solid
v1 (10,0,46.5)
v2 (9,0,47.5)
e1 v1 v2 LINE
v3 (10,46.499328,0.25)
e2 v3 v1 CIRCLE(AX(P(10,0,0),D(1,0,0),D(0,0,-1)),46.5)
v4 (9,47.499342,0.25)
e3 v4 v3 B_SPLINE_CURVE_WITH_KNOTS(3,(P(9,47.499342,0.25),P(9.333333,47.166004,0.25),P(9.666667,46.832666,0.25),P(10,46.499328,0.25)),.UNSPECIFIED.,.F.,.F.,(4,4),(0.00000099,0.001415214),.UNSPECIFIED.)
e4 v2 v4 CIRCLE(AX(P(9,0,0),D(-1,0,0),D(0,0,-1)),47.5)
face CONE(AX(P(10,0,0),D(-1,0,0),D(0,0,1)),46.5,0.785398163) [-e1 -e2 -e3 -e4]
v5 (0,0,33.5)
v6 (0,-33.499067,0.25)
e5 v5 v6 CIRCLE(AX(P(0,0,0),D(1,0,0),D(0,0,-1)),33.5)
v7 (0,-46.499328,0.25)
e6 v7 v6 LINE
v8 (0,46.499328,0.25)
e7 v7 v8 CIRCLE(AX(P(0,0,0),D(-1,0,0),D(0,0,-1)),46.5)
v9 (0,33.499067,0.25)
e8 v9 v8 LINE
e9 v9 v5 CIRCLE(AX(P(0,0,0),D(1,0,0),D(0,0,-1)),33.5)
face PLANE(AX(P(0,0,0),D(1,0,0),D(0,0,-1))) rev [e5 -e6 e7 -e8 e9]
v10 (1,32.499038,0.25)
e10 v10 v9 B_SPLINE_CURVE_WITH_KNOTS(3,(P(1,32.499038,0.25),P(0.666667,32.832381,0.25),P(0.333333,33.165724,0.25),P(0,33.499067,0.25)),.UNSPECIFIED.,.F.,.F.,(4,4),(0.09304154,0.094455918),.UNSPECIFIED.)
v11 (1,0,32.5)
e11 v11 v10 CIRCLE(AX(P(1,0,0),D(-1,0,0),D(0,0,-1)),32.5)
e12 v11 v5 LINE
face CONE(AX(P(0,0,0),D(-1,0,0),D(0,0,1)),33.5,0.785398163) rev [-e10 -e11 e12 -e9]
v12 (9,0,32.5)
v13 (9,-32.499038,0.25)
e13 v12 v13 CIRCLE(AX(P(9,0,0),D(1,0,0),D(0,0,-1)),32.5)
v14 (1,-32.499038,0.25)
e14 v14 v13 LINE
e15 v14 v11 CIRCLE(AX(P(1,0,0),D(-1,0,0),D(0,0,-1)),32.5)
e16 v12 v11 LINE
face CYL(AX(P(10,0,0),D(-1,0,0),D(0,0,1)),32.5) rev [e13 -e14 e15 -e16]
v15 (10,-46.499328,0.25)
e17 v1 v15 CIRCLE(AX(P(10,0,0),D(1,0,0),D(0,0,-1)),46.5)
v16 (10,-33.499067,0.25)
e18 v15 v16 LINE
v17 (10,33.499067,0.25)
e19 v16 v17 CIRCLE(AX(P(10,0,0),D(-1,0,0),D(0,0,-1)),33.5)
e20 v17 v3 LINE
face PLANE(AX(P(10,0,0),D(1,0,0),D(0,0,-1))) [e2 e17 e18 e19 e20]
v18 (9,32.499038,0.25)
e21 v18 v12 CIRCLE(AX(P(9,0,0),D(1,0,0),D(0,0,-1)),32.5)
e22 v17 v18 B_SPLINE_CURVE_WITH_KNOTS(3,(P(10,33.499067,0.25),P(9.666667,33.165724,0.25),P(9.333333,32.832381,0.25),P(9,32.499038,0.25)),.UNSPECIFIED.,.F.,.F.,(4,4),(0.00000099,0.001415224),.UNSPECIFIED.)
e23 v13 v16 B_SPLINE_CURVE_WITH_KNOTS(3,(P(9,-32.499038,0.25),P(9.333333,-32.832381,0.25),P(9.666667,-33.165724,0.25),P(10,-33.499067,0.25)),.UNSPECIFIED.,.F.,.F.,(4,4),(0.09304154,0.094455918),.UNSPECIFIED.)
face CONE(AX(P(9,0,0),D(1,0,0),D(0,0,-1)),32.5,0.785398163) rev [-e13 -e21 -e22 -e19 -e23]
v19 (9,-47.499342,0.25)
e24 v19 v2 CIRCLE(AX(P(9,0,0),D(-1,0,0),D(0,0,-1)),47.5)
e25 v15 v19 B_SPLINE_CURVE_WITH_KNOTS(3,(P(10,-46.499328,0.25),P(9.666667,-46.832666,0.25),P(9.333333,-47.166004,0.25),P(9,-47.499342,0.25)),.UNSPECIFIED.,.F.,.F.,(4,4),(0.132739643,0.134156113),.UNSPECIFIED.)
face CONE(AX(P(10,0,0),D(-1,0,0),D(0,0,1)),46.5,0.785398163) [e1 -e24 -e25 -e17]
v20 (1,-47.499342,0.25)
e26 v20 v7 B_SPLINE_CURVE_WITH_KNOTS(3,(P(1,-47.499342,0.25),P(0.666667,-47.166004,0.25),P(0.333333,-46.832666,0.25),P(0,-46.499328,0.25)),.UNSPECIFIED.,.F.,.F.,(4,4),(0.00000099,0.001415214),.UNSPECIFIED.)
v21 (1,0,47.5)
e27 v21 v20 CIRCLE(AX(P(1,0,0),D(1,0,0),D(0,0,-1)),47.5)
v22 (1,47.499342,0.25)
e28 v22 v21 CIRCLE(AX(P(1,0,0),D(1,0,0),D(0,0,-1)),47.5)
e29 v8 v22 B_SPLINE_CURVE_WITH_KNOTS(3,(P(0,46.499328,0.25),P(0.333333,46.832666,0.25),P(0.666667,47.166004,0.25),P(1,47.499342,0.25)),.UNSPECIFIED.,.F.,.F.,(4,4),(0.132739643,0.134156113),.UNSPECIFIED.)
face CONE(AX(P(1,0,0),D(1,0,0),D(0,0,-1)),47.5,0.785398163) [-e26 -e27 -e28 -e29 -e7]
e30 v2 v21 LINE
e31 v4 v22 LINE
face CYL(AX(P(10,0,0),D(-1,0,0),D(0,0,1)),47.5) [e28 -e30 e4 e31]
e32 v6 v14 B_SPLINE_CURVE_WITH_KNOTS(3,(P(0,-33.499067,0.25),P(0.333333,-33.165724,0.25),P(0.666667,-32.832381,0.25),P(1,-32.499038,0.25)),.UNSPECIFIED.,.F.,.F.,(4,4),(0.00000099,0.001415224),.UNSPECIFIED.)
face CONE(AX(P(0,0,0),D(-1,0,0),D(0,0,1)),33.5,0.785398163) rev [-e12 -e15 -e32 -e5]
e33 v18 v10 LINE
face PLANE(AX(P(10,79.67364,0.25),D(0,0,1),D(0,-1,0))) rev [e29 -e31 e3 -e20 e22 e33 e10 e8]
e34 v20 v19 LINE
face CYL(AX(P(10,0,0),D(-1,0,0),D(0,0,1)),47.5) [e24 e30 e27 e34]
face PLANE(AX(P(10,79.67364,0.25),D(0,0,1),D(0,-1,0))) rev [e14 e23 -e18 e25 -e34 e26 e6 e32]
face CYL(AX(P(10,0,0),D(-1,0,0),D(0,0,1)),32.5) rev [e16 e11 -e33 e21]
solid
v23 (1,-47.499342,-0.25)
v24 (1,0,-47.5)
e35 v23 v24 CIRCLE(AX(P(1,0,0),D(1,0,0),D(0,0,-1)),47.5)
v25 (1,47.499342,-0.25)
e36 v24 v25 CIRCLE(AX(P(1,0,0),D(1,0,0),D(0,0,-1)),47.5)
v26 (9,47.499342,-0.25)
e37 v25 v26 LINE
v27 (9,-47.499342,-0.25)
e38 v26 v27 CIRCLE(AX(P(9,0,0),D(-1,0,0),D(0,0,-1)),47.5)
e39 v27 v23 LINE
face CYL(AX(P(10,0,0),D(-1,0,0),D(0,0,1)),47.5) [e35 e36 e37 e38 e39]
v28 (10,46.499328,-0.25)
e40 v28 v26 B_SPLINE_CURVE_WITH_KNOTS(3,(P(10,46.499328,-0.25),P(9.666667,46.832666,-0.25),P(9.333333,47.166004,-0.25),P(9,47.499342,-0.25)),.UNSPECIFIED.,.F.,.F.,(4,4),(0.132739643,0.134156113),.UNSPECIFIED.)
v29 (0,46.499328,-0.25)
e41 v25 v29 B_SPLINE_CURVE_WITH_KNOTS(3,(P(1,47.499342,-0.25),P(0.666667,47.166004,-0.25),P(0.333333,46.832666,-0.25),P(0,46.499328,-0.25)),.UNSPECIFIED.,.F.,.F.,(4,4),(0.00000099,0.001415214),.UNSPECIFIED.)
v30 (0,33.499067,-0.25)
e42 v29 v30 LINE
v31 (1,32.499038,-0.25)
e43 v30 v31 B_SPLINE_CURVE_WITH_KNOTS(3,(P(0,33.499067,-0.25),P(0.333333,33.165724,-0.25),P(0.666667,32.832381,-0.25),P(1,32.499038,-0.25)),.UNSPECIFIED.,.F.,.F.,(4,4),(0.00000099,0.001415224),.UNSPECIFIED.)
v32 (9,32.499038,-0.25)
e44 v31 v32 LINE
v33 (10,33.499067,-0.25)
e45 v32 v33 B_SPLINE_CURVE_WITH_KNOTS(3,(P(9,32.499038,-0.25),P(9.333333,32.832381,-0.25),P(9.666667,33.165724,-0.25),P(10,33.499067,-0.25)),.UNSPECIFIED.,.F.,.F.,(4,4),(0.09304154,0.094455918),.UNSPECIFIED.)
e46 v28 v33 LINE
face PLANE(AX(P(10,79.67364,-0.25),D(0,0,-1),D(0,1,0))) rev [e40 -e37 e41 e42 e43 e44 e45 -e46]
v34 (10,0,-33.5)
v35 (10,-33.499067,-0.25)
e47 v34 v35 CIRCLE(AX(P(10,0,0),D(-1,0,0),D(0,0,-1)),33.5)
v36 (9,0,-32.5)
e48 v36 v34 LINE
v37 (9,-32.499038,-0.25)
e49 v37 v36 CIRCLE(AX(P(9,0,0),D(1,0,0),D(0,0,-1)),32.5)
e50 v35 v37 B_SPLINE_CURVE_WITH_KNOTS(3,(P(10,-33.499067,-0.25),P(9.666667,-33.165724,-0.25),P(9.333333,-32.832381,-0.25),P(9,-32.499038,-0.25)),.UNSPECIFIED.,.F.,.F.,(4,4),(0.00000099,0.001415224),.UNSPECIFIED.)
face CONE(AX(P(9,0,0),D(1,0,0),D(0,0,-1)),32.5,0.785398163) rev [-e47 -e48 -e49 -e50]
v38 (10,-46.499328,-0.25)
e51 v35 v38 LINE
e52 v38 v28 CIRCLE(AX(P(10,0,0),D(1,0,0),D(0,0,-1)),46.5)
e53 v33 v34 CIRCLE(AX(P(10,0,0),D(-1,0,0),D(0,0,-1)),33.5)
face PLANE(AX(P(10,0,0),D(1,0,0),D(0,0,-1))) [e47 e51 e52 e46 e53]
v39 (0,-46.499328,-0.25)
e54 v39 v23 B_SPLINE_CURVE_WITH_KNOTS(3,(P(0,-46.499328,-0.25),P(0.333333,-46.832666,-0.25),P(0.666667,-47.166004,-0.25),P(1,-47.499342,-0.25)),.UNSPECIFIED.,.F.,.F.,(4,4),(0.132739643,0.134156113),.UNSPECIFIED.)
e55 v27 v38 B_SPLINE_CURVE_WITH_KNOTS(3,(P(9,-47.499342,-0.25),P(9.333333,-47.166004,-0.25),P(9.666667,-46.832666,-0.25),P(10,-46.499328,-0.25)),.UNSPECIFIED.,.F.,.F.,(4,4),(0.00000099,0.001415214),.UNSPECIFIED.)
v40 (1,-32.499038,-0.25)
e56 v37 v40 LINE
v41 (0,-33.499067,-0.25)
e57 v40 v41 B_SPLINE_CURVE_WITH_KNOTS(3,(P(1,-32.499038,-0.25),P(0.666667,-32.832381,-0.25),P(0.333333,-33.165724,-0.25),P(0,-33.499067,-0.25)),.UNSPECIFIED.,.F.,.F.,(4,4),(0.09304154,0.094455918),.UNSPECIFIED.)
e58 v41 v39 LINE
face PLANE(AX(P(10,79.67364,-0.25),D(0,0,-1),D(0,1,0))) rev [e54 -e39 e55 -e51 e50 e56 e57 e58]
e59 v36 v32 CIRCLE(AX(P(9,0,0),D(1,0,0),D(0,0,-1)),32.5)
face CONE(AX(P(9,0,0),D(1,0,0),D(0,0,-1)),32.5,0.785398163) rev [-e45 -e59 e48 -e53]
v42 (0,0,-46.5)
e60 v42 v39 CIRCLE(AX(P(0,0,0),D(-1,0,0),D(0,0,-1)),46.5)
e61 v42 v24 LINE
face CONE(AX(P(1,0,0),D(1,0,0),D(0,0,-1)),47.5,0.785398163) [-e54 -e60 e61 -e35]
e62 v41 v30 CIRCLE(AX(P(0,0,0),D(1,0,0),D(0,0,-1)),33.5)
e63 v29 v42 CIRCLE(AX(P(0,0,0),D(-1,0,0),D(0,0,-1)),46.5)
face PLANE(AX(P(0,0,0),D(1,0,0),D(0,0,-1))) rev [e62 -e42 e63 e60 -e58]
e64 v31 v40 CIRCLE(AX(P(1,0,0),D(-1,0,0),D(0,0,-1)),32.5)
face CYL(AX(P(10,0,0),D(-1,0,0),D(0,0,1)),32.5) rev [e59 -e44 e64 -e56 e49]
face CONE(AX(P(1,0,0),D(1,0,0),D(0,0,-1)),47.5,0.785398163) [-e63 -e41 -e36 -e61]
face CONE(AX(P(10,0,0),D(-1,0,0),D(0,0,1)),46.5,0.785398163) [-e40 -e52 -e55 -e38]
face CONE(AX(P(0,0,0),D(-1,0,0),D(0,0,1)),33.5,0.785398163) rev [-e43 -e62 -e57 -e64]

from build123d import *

# Parameters (mm, degrees)
SKETCH_1_R          = 47.5
SKETCH_1_R_2        = 32.5
EXTRUDE_1_DEPTH     = 10
CHAMFER_1_SIZE      = 1
SKETCH_2_W          = 0.5
SKETCH_2_H          = 159.347280508
CUT_EXTRUDE_1_DEPTH = 68.915388536


with BuildPart() as part:
    # 草图1 → 凸台-拉伸1 (new body)
    with BuildSketch(Plane(origin=(0, 0, 0), x_dir=(0, 0, -1), z_dir=(1, 0, 0))):
        Circle(SKETCH_1_R)
        Circle(SKETCH_1_R_2, mode=Mode.SUBTRACT)
    extrude(amount=EXTRUDE_1_DEPTH)

    # 倒角1
    chamfer_1_edges = [part.edges().sort_by_distance(p)[0] for p in [
        (0, 0, 47.5),
        (10, 0, 47.5),
        (0, 0, 32.5),
        (10, 0, 32.5),
    ]]
    chamfer(chamfer_1_edges, length=CHAMFER_1_SIZE)

    # 草图2 → 切除-拉伸1 (cut, through all)
    with BuildSketch(Plane.ZY):
        Rectangle(SKETCH_2_W, SKETCH_2_H)
    extrude(amount=-CUT_EXTRUDE_1_DEPTH, mode=Mode.SUBTRACT)


with BuildPart() as cut_extrude_1_piece_1:
    # of the separate pieces the step leaves, piece 1, a body of its own (cut_extrude_1_pieces)
    add(part.part.solids().sort_by_distance((1, -47.499342101, -0.25))[0])


with BuildPart() as cut_extrude_1_piece_2:
    # of the separate pieces the step leaves, piece 2, a body of its own (cut_extrude_1_pieces)
    add(part.part.solids().sort_by_distance((1, 47.499342101, 0.25))[0])


solid = Compound([cut_extrude_1_piece_1.part, cut_extrude_1_piece_2.part])
